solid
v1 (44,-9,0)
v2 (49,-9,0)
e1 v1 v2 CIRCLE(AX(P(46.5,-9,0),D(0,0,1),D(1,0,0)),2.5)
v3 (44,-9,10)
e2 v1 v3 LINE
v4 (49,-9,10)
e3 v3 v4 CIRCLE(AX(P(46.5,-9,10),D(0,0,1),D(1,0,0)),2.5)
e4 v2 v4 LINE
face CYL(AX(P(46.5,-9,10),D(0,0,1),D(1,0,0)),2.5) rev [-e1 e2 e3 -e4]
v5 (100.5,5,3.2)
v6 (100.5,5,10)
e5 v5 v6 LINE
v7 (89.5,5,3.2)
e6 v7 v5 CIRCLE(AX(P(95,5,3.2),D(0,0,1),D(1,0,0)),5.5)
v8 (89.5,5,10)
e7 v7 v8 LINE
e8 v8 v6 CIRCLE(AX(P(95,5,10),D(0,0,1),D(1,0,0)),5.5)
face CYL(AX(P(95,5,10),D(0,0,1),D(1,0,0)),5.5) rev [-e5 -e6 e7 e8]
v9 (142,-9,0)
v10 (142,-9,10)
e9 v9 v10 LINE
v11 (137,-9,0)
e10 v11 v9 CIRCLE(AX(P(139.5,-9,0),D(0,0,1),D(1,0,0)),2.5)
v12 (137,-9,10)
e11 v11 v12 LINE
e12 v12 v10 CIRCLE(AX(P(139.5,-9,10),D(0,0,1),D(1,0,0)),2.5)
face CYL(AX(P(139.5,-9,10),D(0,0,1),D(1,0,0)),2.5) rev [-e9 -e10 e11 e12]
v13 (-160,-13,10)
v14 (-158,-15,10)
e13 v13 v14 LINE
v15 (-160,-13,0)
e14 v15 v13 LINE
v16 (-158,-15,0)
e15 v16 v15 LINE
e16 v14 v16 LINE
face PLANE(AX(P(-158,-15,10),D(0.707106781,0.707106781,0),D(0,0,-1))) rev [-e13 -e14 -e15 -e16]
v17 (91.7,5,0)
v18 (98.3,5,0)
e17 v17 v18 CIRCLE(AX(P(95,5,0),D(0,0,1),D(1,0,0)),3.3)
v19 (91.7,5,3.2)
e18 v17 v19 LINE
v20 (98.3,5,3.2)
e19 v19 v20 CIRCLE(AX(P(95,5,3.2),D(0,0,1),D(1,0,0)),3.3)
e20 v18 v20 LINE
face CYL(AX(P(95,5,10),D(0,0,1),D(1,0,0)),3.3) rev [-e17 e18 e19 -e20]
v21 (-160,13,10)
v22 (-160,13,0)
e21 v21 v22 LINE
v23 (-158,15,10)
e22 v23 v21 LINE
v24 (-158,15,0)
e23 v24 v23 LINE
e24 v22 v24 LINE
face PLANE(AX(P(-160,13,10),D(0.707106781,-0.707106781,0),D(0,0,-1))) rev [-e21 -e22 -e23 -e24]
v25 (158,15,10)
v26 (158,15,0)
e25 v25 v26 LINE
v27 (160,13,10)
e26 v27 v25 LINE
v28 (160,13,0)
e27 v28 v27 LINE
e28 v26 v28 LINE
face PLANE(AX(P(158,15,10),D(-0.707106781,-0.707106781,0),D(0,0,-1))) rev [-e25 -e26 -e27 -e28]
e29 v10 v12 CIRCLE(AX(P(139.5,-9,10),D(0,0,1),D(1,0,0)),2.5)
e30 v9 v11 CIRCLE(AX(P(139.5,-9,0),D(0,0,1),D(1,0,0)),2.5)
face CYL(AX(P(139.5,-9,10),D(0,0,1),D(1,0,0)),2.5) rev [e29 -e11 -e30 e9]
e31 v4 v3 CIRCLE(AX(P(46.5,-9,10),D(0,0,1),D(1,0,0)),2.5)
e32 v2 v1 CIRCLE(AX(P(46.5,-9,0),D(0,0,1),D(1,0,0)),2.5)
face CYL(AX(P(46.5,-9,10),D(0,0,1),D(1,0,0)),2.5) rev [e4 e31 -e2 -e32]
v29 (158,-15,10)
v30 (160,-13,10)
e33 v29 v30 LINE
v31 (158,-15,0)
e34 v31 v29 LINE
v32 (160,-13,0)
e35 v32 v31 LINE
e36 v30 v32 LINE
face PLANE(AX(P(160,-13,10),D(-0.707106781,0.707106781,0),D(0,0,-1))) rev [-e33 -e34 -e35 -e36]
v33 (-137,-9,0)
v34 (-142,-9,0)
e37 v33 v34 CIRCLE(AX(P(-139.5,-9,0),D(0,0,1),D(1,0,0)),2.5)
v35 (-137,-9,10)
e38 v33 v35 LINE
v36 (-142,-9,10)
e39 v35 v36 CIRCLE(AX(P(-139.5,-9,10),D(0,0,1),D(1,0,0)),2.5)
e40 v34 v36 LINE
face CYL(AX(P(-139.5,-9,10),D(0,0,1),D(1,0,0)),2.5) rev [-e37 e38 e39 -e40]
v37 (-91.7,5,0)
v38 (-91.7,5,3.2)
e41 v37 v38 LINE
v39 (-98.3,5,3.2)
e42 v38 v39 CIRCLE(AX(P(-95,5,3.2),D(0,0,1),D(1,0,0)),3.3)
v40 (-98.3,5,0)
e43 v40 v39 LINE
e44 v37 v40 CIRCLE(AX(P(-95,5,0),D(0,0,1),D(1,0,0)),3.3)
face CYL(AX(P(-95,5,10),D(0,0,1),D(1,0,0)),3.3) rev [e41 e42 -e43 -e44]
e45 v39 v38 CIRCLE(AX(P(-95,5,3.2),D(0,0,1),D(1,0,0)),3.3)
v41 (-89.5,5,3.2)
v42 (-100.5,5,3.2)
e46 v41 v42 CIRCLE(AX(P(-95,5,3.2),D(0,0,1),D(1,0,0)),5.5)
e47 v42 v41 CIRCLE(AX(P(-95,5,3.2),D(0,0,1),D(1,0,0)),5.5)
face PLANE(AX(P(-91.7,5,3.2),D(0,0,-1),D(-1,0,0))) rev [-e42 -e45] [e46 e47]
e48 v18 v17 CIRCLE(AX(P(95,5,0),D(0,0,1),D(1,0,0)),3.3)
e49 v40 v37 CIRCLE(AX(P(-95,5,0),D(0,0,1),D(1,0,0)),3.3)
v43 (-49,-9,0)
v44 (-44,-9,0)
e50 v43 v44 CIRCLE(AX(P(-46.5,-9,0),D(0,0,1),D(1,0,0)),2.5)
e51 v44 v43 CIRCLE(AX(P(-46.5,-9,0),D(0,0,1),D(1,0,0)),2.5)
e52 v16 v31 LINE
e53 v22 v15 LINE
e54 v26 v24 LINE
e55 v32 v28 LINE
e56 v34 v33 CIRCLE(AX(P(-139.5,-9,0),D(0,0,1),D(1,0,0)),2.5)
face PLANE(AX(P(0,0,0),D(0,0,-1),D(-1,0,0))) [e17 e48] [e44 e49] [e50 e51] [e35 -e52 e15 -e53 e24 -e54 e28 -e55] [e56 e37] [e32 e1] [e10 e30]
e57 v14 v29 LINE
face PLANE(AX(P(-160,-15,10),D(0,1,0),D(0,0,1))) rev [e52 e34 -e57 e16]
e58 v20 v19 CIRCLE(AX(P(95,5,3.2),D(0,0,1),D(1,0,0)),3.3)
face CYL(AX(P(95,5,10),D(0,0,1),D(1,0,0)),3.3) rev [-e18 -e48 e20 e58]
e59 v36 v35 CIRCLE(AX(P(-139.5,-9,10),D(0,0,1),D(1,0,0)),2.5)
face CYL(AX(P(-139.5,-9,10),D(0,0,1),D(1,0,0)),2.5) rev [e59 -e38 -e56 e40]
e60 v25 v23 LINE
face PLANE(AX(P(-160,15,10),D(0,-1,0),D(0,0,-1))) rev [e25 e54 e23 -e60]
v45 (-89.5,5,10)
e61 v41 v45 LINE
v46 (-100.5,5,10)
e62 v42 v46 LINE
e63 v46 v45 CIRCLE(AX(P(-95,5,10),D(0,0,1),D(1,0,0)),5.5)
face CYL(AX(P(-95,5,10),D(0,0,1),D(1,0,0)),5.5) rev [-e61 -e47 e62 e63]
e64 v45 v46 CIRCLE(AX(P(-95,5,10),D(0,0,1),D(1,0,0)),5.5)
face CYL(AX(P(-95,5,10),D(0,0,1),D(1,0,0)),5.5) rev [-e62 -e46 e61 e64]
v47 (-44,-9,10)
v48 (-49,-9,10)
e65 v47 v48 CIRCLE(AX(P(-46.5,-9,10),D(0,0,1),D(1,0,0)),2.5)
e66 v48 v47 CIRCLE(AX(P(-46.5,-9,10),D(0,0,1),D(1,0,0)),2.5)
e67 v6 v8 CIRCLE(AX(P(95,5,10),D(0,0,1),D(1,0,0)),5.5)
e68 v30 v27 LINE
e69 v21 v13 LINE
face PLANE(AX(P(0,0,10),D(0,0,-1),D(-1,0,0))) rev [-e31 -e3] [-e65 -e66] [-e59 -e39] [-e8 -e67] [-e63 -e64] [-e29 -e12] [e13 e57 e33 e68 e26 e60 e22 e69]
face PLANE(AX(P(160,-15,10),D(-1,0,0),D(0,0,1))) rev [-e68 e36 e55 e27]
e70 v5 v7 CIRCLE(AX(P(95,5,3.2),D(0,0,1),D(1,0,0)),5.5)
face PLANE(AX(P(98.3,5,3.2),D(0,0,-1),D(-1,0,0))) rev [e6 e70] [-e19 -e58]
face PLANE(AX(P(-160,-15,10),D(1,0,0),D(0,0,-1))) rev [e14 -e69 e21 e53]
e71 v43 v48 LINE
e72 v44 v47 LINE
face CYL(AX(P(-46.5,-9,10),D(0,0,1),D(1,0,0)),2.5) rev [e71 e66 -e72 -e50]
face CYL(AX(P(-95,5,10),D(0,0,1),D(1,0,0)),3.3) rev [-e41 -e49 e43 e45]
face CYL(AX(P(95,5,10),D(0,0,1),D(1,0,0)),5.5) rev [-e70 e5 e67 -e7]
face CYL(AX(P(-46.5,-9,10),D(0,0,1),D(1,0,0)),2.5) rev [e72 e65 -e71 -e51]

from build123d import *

# Parameters (mm, degrees)
SKETCH1_W           = 320
SKETCH1_H           = 30
BOSS_EXTRUDE1_DEPTH = 10
CHAMFER1_SIZE       = 2
M6_TAPPED_HOLE1_D   = 5
HOLE1_D             = 6.6
HOLE1_CBORE_D       = 11
HOLE1_CBORE_DEPTH   = 6.8


with BuildPart() as part:
    # Sketch1 → Boss-Extrude1 (new body)
    with BuildSketch(Plane.XY):
        Rectangle(SKETCH1_W, SKETCH1_H)
    extrude(amount=BOSS_EXTRUDE1_DEPTH)

    # Chamfer1
    chamfer1_edges = [part.edges().sort_by_distance(p)[0] for p in [
        (160, -15, 5),
        (-160, -15, 5),
        (-160, 15, 5),
        (160, 15, 5),
    ]]
    chamfer(chamfer1_edges, length=CHAMFER1_SIZE)

    # M6 Tapped Hole1 (through all)
    with Locations(Plane.XY.offset(10)):
        with Locations((-139.5, -9), (-46.5, -9), (46.5, -9), (139.5, -9)):
            Hole(M6_TAPPED_HOLE1_D / 2)

    # Hole1 (through all)
    with Locations(Plane.XY.offset(10)):
        with Locations((-95, 5), (95, 5)):
            CounterBoreHole(HOLE1_D / 2, HOLE1_CBORE_D / 2, HOLE1_CBORE_DEPTH)


solid = part.part
